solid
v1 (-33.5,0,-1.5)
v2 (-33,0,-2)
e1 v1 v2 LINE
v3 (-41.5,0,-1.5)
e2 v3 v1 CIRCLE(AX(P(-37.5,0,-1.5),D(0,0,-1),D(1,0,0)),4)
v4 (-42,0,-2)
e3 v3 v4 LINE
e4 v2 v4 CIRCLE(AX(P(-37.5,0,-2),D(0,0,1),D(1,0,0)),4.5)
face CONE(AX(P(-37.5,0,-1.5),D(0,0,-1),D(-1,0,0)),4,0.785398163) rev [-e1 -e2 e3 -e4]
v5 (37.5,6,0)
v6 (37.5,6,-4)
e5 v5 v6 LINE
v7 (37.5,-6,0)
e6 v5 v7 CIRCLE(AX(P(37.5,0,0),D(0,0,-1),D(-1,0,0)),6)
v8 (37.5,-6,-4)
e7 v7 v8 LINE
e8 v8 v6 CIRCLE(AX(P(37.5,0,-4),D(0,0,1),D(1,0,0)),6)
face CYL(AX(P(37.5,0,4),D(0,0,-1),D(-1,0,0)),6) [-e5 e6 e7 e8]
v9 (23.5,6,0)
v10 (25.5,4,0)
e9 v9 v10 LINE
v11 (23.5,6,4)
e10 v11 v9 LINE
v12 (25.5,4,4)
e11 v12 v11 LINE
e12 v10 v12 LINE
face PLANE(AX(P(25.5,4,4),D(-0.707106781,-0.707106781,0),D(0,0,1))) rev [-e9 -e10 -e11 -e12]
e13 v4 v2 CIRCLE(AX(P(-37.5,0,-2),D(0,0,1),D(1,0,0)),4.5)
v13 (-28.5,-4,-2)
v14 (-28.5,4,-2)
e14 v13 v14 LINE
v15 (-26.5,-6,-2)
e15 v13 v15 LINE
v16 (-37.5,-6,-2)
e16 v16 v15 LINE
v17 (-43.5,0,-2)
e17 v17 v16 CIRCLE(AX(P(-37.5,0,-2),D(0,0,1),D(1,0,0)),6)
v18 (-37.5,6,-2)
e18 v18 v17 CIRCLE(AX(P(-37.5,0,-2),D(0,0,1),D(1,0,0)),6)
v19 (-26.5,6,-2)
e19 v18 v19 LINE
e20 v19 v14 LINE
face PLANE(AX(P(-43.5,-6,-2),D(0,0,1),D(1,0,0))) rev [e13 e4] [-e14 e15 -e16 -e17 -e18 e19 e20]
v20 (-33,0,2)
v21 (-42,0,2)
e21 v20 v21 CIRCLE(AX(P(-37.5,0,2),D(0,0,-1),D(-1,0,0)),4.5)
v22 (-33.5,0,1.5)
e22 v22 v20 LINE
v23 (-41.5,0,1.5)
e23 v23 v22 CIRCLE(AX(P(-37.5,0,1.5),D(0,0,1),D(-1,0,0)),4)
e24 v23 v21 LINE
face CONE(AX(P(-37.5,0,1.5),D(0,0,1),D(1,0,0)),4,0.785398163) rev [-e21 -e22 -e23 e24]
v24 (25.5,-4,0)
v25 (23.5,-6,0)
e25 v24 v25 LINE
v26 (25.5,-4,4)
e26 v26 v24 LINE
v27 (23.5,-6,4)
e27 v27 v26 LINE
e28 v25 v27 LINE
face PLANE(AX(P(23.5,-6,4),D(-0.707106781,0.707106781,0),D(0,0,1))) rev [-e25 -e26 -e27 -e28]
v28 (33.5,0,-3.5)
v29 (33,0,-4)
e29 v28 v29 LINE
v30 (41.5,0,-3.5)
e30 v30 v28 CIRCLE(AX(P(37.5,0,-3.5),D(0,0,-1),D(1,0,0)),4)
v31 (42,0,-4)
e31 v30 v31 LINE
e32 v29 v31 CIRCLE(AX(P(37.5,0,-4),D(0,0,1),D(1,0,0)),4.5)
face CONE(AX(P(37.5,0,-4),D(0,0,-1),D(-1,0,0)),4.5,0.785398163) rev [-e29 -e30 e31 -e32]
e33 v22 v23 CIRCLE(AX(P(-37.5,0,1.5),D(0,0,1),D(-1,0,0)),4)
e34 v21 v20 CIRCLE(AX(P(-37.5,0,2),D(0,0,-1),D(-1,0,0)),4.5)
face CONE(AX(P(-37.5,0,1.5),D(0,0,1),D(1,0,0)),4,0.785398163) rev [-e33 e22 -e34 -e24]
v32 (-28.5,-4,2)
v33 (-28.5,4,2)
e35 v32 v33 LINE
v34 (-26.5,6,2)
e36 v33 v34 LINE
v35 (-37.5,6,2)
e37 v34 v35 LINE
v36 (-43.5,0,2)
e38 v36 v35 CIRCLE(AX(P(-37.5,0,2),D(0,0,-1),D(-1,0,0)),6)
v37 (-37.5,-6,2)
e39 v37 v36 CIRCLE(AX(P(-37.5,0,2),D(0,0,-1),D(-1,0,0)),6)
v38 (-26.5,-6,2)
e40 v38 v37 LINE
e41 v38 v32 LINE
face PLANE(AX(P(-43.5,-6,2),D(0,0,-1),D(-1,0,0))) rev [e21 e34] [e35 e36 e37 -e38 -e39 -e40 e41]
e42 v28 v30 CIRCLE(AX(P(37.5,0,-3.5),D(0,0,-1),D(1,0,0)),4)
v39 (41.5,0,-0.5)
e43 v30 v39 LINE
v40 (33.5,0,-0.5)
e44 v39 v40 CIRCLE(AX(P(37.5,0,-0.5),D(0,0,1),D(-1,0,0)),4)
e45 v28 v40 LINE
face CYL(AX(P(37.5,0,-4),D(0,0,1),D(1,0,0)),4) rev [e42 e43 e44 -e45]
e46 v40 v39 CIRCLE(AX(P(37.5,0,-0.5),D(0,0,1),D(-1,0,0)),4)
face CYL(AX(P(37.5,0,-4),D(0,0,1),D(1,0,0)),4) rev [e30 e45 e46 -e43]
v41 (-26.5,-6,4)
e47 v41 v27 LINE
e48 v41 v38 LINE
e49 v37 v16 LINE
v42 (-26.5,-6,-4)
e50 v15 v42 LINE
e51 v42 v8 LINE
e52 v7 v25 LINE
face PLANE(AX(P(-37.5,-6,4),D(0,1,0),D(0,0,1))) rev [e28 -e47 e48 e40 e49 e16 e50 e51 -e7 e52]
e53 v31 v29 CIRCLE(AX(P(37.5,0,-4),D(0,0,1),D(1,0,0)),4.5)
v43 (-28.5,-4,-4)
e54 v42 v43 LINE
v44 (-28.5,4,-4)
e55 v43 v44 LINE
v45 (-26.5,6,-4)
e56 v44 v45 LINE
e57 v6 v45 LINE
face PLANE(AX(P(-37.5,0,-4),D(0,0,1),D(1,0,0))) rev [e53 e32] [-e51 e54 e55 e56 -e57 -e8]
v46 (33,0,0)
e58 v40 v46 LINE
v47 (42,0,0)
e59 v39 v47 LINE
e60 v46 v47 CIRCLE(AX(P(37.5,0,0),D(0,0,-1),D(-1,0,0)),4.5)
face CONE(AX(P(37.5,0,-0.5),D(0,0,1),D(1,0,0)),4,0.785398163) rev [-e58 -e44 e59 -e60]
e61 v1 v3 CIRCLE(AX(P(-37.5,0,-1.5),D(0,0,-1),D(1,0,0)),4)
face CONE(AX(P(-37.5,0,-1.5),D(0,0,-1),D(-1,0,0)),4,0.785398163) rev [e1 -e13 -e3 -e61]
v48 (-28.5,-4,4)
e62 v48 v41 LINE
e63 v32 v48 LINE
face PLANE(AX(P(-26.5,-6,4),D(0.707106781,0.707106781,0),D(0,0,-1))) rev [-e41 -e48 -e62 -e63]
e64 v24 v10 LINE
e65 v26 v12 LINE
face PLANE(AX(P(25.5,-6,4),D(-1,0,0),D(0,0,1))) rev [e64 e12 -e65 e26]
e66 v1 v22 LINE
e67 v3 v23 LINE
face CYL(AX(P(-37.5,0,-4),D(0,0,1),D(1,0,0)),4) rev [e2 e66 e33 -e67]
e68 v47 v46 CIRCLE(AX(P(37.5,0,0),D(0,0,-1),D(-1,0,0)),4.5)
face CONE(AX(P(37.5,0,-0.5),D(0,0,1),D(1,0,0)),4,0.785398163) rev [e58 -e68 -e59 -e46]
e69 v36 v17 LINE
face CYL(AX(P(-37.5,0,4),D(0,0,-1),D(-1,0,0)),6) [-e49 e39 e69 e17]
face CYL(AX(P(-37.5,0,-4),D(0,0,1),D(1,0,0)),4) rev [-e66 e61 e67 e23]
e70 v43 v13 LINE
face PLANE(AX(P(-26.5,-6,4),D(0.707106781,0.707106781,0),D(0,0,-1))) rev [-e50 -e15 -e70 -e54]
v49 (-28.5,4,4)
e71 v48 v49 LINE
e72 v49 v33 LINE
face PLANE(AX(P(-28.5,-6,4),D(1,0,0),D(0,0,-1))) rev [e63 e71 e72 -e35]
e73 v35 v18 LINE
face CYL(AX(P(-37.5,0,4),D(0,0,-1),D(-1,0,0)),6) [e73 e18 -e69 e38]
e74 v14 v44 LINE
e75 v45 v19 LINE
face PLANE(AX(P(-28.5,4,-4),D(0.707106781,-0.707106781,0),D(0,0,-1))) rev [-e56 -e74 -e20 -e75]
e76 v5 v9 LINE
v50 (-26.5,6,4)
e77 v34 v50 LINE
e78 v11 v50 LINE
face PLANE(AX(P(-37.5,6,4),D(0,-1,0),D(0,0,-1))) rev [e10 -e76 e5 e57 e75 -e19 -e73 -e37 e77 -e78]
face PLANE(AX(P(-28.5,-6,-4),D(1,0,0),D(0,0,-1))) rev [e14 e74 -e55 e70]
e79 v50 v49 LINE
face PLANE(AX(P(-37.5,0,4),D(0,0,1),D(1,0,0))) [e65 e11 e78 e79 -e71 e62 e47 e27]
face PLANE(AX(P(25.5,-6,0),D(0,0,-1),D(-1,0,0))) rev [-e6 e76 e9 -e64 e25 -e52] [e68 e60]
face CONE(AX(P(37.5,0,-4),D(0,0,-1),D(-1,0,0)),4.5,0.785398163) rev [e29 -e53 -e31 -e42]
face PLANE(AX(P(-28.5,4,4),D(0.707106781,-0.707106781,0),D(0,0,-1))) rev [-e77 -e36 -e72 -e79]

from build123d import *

# Parameters (mm, degrees)
BOSS_EXTRUDE1_DEPTH = 4
SKETCH2_R           = 4
CUT_EXTRUDE2_DEPTH  = 45.634627813
SKETCH3_W           = 18
SKETCH3_H           = 4
SKETCH3_W_2         = 15
SKETCH3_H_2         = 2
CUT_EXTRUDE3_DEPTH  = 46.30176597
CHAMFER1_SIZE       = 2
CHAMFER2_SIZE       = 0.5


with BuildPart() as part:
    # Sketch1 → Boss-Extrude1 (new, symmetric)
    with BuildSketch(Plane.XY):
        with BuildLine():
            Line((-37.5, 6), (37.5, 6))
            ThreePointArc((37.5, 6), (43.5, 0), (37.5, -6))
            Line((37.5, -6), (-37.5, -6))
            ThreePointArc((-37.5, -6), (-43.5, 0), (-37.5, 6))
        make_face()
    extrude(amount=BOSS_EXTRUDE1_DEPTH, both=True)

    # Sketch2 → Cut-Extrude2 (cut, through all)
    with BuildSketch(Plane.XY.offset(4)):
        with Locations((37.5, 0)):
            Circle(SKETCH2_R)
        with Locations((-37.5, 0)):
            Circle(SKETCH2_R)
    extrude(amount=-CUT_EXTRUDE2_DEPTH, mode=Mode.SUBTRACT)

    # Sketch3 → Cut-Extrude3 (cut, through all)
    with BuildSketch(Plane(origin=(0, 6, 0), x_dir=(1, 0, 0), z_dir=(0, 1, 0))):
        with Locations((34.5, -2)):
            Rectangle(SKETCH3_W, SKETCH3_H)
        with Locations((-36, -3)):
            Rectangle(SKETCH3_W_2, SKETCH3_H_2)
        with Locations((-36, 3)):
            Rectangle(SKETCH3_W_2, SKETCH3_H_2)
    extrude(amount=-CUT_EXTRUDE3_DEPTH, mode=Mode.SUBTRACT)

    # Chamfer1
    chamfer1_edges = [part.edges().sort_by_distance(p)[0] for p in [
        (25.5, -6, 2),
        (25.5, 6, 2),
        (-28.5, 6, 3),
        (-28.5, -6, 3),
        (-28.5, -6, -3),
        (-28.5, 6, -3),
    ]]
    chamfer(chamfer1_edges, length=CHAMFER1_SIZE)

    # Chamfer2
    chamfer2_edges = [part.edges().sort_by_distance(p)[0] for p in [
        (33.5, 0, -4),
        (33.5, 0, 0),
        (-41.5, 0, 2),
        (-41.5, 0, -2),
    ]]
    chamfer(chamfer2_edges, length=CHAMFER2_SIZE)


solid = part.part
